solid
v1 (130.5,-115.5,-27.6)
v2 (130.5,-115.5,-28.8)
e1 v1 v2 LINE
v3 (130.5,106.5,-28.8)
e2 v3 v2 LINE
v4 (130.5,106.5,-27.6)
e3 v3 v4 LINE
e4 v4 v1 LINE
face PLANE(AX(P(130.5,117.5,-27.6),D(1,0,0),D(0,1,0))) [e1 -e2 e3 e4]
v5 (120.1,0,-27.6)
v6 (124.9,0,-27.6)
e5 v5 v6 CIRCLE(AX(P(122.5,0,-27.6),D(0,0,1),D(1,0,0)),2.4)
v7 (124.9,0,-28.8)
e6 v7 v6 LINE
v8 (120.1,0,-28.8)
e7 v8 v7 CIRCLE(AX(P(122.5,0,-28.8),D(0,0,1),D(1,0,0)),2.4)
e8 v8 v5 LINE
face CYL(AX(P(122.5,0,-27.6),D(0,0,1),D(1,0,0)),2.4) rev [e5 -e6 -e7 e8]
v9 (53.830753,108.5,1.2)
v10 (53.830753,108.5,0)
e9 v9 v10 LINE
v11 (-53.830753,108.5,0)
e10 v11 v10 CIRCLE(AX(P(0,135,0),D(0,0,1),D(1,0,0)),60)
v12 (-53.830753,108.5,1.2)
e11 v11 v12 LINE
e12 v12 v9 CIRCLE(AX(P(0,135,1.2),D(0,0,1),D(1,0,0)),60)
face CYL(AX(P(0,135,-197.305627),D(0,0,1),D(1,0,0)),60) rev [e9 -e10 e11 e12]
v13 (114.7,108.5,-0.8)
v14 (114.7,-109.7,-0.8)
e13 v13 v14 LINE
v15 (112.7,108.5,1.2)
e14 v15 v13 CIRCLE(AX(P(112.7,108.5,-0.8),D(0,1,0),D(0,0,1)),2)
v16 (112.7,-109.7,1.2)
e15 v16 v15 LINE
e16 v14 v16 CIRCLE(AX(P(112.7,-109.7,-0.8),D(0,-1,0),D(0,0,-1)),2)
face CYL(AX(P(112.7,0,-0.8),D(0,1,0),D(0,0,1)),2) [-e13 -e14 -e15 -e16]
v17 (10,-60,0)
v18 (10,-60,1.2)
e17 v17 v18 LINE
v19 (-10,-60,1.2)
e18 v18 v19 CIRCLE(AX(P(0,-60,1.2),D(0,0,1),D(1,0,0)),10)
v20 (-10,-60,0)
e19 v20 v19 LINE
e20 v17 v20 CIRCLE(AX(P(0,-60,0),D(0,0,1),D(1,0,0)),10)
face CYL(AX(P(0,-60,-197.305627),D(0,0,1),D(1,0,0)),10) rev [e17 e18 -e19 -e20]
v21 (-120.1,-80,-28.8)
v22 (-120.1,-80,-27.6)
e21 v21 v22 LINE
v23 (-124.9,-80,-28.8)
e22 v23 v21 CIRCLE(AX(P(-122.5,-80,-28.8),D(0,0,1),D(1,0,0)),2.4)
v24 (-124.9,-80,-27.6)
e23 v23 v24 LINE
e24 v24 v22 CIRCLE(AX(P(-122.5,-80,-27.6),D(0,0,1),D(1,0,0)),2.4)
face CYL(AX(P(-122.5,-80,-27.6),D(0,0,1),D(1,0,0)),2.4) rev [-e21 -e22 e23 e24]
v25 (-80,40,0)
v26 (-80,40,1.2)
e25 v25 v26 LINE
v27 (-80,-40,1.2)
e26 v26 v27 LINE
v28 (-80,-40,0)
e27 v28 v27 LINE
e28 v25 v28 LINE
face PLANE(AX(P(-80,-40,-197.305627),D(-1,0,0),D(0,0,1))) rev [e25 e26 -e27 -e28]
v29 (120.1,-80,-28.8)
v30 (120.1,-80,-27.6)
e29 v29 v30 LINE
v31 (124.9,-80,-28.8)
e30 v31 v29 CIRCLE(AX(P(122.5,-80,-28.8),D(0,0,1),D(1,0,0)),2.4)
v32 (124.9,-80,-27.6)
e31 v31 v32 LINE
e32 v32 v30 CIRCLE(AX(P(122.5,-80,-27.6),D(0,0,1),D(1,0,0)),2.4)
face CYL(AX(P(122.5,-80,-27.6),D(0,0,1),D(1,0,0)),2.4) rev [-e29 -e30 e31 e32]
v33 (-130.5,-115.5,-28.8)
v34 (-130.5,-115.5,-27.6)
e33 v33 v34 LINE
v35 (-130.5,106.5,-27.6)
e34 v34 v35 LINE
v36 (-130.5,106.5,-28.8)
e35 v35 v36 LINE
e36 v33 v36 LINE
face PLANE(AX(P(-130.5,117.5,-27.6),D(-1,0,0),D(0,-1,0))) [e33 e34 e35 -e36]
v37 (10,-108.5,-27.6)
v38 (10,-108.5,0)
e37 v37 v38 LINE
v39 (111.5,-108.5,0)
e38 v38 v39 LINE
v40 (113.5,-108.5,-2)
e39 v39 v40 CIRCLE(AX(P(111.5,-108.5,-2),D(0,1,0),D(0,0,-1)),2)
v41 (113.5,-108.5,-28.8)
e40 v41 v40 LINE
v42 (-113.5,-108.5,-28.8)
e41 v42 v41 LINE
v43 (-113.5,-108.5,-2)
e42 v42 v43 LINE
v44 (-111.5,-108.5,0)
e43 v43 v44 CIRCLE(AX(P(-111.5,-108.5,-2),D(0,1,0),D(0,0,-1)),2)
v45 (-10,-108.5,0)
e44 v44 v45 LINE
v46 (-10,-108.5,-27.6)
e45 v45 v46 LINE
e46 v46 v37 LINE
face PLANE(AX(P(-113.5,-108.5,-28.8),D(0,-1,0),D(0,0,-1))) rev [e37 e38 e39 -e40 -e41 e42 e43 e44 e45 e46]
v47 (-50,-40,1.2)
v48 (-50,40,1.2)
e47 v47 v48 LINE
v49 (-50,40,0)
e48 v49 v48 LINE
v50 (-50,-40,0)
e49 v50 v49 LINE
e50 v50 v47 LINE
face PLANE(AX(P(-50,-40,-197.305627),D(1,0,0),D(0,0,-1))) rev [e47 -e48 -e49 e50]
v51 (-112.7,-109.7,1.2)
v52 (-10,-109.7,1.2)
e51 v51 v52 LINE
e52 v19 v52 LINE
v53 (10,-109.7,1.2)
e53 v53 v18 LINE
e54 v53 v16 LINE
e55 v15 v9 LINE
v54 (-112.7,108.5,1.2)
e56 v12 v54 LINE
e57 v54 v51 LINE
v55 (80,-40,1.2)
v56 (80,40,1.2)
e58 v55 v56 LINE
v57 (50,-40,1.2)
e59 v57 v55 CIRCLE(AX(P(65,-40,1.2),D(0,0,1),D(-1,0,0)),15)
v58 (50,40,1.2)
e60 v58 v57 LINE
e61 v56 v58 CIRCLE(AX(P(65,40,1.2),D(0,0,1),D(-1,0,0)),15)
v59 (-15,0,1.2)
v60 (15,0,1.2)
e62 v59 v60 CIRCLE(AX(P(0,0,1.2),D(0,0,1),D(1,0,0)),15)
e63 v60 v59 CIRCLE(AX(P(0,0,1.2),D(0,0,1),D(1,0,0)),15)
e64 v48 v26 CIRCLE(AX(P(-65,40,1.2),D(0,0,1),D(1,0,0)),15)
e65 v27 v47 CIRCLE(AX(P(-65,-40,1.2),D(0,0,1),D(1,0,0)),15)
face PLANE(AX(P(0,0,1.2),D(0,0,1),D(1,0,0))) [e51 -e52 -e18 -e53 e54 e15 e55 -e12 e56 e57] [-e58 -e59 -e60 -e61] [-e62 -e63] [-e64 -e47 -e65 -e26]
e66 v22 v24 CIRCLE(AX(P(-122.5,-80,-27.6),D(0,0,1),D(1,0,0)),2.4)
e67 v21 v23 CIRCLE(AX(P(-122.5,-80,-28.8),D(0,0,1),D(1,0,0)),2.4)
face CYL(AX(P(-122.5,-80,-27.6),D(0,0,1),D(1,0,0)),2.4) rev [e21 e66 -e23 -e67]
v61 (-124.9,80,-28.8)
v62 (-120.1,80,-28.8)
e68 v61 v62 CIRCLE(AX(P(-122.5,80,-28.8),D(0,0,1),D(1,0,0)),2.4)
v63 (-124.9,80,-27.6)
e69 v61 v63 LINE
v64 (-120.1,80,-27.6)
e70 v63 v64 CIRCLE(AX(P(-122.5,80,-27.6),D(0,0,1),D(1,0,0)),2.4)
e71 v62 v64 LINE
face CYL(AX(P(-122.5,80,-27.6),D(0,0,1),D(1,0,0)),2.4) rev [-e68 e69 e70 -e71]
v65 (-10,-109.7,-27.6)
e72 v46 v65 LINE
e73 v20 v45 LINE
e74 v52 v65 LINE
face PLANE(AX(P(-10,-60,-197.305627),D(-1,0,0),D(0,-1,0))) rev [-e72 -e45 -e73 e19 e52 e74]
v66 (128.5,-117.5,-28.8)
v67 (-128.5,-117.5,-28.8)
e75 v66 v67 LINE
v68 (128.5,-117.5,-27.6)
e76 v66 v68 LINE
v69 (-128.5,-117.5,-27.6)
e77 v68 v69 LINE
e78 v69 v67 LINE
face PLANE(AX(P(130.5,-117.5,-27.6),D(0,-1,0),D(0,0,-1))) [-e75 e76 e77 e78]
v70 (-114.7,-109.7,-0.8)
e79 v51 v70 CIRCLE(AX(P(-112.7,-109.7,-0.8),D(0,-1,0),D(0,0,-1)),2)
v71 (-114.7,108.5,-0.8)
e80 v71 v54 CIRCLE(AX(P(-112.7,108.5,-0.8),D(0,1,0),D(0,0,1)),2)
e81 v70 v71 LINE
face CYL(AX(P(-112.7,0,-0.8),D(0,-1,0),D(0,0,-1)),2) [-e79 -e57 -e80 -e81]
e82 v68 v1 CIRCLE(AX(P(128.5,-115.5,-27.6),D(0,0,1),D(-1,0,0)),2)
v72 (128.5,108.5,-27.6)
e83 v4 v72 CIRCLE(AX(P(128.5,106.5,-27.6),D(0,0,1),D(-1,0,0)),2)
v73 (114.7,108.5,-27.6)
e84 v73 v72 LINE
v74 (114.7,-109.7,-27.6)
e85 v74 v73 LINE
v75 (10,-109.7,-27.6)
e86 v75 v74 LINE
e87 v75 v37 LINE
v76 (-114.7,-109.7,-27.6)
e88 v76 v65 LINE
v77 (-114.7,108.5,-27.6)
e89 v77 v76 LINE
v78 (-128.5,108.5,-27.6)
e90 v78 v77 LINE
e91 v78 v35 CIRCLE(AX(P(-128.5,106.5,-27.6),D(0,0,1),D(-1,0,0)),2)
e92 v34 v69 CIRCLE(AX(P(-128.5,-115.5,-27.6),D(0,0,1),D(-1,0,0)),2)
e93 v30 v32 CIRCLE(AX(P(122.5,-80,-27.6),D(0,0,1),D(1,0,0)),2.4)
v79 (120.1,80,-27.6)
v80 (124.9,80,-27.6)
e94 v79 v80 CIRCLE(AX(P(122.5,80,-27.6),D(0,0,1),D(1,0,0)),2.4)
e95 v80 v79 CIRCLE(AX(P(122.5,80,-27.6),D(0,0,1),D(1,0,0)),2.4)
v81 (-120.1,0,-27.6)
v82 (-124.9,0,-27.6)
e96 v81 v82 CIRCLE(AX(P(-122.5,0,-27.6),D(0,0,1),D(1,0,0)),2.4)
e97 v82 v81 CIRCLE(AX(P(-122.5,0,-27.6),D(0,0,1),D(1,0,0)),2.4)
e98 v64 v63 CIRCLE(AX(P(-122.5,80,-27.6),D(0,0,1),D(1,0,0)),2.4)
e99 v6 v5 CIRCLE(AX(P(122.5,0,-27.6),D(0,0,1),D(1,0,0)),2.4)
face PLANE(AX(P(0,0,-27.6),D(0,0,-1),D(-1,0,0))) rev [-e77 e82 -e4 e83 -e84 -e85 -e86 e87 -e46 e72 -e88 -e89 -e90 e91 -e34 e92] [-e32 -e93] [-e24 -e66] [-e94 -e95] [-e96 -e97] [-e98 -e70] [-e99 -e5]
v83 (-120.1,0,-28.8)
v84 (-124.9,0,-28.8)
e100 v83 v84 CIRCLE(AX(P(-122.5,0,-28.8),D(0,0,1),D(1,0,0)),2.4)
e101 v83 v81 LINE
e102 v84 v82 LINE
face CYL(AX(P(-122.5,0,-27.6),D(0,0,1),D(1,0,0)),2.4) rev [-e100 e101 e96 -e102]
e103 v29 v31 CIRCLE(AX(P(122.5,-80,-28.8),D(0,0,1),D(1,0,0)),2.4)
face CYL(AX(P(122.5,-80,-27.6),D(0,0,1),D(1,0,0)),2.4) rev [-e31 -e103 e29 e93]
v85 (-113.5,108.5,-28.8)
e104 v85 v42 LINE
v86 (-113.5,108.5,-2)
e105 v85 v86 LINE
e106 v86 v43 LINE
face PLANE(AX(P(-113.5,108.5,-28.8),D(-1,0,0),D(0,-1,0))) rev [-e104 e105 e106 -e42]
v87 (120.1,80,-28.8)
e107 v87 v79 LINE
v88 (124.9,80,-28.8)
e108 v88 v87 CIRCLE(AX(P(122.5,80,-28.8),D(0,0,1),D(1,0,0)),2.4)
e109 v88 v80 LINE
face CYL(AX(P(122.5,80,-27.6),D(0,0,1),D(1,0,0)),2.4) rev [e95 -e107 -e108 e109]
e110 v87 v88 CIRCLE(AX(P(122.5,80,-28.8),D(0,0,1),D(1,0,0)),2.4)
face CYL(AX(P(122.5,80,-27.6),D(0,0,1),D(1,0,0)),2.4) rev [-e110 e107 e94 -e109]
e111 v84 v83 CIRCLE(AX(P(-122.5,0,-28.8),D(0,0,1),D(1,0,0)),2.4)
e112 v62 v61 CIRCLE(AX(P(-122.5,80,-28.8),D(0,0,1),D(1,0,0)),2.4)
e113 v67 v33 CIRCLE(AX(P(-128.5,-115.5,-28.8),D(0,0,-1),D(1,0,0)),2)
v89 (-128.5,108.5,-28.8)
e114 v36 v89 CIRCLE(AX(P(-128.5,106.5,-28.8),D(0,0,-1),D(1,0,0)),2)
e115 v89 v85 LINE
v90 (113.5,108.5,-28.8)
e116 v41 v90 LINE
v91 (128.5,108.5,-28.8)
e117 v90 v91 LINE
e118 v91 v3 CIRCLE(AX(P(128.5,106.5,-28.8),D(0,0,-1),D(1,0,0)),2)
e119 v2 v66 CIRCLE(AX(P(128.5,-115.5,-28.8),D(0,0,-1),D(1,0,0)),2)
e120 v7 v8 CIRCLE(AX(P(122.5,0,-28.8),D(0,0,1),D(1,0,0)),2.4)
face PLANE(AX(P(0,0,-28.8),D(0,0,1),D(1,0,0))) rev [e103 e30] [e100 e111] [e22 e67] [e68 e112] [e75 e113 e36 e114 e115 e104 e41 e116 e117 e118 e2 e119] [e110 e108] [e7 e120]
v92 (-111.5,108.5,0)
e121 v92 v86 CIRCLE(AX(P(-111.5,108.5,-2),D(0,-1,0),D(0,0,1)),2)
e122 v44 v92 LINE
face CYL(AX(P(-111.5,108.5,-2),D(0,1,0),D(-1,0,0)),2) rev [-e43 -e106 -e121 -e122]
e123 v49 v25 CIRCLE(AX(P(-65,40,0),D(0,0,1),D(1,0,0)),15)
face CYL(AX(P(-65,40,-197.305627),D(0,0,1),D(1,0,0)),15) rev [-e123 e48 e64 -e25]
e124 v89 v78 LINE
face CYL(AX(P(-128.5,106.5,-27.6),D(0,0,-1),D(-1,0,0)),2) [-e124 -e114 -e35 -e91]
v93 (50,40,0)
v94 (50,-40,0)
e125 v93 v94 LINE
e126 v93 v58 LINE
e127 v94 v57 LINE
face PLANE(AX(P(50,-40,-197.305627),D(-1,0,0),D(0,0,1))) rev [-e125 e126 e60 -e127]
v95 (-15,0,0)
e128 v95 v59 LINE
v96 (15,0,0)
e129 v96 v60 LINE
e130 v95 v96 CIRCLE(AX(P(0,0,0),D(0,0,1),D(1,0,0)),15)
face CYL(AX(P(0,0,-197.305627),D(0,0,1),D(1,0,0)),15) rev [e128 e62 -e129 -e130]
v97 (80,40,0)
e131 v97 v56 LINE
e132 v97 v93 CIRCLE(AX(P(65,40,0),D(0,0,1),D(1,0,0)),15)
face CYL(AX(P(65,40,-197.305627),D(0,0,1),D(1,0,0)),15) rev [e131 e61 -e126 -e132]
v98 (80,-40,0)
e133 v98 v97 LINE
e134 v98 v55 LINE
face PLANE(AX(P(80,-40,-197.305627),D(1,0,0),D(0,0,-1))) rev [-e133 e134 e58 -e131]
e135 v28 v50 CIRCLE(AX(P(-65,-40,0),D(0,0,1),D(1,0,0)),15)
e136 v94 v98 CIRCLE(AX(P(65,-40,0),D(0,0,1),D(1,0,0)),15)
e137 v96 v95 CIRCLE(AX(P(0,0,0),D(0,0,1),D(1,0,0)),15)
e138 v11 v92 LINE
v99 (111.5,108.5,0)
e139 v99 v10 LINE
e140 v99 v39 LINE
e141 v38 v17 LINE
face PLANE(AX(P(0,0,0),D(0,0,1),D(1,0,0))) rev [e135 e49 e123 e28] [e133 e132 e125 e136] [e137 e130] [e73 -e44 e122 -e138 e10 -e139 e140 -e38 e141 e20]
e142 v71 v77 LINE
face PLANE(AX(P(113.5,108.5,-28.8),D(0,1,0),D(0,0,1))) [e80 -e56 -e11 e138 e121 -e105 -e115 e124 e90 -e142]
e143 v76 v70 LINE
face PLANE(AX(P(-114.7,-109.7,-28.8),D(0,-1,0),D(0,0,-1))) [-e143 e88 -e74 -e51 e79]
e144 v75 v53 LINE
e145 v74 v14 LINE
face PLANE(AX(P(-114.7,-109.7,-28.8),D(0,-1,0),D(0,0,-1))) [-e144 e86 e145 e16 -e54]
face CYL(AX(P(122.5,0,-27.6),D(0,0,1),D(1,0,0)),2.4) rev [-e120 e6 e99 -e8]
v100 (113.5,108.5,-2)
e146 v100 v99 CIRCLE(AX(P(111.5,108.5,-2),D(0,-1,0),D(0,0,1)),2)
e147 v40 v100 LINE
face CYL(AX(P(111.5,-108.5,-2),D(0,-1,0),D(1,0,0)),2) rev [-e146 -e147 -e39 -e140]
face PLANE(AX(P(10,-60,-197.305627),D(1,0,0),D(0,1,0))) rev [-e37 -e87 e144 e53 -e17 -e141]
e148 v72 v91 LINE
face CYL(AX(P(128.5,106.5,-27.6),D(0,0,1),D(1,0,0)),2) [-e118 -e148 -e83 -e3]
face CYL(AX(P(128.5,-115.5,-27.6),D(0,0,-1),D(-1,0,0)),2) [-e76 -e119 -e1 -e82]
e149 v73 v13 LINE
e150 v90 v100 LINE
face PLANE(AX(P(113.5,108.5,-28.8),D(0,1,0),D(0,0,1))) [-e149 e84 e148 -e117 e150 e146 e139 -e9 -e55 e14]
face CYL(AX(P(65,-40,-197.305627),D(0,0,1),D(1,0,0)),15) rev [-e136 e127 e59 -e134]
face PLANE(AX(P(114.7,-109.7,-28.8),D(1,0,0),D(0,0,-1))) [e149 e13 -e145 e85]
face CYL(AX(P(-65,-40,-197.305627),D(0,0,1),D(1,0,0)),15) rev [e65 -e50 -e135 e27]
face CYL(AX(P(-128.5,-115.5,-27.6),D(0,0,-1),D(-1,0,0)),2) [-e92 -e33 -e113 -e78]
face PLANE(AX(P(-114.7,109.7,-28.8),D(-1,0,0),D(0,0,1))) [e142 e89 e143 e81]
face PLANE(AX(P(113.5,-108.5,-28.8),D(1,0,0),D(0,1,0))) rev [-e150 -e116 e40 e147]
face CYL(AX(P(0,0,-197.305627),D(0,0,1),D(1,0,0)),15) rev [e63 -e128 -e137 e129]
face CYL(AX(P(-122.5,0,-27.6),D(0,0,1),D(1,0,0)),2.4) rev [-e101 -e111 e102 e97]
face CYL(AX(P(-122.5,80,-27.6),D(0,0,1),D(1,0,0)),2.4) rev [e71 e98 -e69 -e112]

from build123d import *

# Parameters (mm, degrees)
SKETCH1_W            = 227
SKETCH1_H            = 217
BOSS_EXTRUDE1_DEPTH  = 1.2
SKETCH21_W           = 229.4
SKETCH21_H           = 219.4
SKETCH21_W_2         = 227
SKETCH21_H_2         = 217
BOSS_EXTRUDE2_DEPTH  = 30
SKETCH22_W           = 261
SKETCH22_H           = 235
SKETCH22_W_2         = 227
SKETCH22_H_2         = 217
BOSS_EXTRUDE3_DEPTH  = 1.2
SKETCH23_W           = 261
SKETCH23_H           = 30
CUT_EXTRUDE1_DEPTH   = 9
CUT_EXTRUDE2_START   = -28.8
SKETCH24_R           = 15
SKETCH24_R_2         = 60
CUT_EXTRUDE2_DEPTH   = 28.8
FILLET1_R            = 2
FILLET2_R            = 2
M4_CLEARANCE_HOLE1_D = 4.8


with BuildPart() as part:
    # Sketch1 → Boss-Extrude1 (new body)
    with BuildSketch(Plane.XY):
        Rectangle(SKETCH1_W, SKETCH1_H)
    extrude(amount=BOSS_EXTRUDE1_DEPTH)

    # Sketch21 → Boss-Extrude2 (add)
    with BuildSketch(Plane.XY.offset(1.2)):
        Rectangle(SKETCH21_W, SKETCH21_H)
        Rectangle(SKETCH21_W_2, SKETCH21_H_2, mode=Mode.SUBTRACT)
    extrude(amount=-BOSS_EXTRUDE2_DEPTH)

    # Sketch22 → Boss-Extrude3 (add)
    with BuildSketch(Plane(origin=(0, 0, -28.8), x_dir=(-1, 0, 0), z_dir=(0, 0, -1))):
        Rectangle(SKETCH22_W, SKETCH22_H)
        Rectangle(SKETCH22_W_2, SKETCH22_H_2, mode=Mode.SUBTRACT)
    extrude(amount=-BOSS_EXTRUDE3_DEPTH)

    # Sketch23 → Cut-Extrude1 (cut)
    with BuildSketch(Plane(origin=(0, 117.5, 0), x_dir=(1, 0, 0), z_dir=(0, 1, 0))):
        with Locations((0, 13.8)):
            Rectangle(SKETCH23_W, SKETCH23_H)
    extrude(amount=-CUT_EXTRUDE1_DEPTH, mode=Mode.SUBTRACT)

    # Sketch24 → Cut-Extrude2 (cut)
    with BuildSketch(Plane.XY.offset(1.2).offset(CUT_EXTRUDE2_START)):
        Circle(SKETCH24_R)
        with Locations((0, 135)):
            Circle(SKETCH24_R_2)
        with BuildLine():
            Line((-80, -40), (-80, 40))
            ThreePointArc((-80, 40), (-65, 55), (-50, 40))
            Line((-50, 40), (-50, -40))
            ThreePointArc((-50, -40), (-65, -55), (-80, -40))
        make_face()
        with BuildLine():
            Line((80, -40), (80, 40))
            ThreePointArc((80, 40), (65, 55), (50, 40))
            Line((50, 40), (50, -40))
            ThreePointArc((50, -40), (65, -55), (80, -40))
        make_face()
        with BuildLine():
            Line((10, -60), (10, -120))
            ThreePointArc((10, -120), (0, -130), (-10, -120))
            Line((-10, -120), (-10, -60))
            ThreePointArc((-10, -60), (0, -50), (10, -60))
        make_face()
    extrude(amount=CUT_EXTRUDE2_DEPTH, mode=Mode.SUBTRACT)

    # Fillet1
    fillet1_edges = [part.edges().sort_by_distance(p)[0] for p in [
        (114.7, -0.6, 1.2),
        (-113.5, 0, 0),
        (113.5, 0, 0),
        (-114.7, -0.6, 1.2),
    ]]
    fillet(fillet1_edges, radius=FILLET1_R)

    # Fillet2
    fillet2_edges = [part.edges().sort_by_distance(p)[0] for p in [
        (-130.5, -117.5, -28.2),
        (130.5, -117.5, -28.2),
        (130.5, 108.5, -28.2),
        (-130.5, 108.5, -28.2),
    ]]
    fillet(fillet2_edges, radius=FILLET2_R)

    # M4 Clearance Hole1 (through all)
    with Locations(Plane.XY.offset(-27.6)):
        with Locations((-122.5, 80)):
            m4_clearance_hole1 = Hole(M4_CLEARANCE_HOLE1_D / 2)

    # Sketch pattern1: M4 Clearance Hole1 at 5 more places
    with Locations((0, -80, 0), (0, -160, 0), (245, -160, 0), (245, -80, 0), (245, 0, 0)):
        add(m4_clearance_hole1, mode=Mode.SUBTRACT)


solid = part.part
